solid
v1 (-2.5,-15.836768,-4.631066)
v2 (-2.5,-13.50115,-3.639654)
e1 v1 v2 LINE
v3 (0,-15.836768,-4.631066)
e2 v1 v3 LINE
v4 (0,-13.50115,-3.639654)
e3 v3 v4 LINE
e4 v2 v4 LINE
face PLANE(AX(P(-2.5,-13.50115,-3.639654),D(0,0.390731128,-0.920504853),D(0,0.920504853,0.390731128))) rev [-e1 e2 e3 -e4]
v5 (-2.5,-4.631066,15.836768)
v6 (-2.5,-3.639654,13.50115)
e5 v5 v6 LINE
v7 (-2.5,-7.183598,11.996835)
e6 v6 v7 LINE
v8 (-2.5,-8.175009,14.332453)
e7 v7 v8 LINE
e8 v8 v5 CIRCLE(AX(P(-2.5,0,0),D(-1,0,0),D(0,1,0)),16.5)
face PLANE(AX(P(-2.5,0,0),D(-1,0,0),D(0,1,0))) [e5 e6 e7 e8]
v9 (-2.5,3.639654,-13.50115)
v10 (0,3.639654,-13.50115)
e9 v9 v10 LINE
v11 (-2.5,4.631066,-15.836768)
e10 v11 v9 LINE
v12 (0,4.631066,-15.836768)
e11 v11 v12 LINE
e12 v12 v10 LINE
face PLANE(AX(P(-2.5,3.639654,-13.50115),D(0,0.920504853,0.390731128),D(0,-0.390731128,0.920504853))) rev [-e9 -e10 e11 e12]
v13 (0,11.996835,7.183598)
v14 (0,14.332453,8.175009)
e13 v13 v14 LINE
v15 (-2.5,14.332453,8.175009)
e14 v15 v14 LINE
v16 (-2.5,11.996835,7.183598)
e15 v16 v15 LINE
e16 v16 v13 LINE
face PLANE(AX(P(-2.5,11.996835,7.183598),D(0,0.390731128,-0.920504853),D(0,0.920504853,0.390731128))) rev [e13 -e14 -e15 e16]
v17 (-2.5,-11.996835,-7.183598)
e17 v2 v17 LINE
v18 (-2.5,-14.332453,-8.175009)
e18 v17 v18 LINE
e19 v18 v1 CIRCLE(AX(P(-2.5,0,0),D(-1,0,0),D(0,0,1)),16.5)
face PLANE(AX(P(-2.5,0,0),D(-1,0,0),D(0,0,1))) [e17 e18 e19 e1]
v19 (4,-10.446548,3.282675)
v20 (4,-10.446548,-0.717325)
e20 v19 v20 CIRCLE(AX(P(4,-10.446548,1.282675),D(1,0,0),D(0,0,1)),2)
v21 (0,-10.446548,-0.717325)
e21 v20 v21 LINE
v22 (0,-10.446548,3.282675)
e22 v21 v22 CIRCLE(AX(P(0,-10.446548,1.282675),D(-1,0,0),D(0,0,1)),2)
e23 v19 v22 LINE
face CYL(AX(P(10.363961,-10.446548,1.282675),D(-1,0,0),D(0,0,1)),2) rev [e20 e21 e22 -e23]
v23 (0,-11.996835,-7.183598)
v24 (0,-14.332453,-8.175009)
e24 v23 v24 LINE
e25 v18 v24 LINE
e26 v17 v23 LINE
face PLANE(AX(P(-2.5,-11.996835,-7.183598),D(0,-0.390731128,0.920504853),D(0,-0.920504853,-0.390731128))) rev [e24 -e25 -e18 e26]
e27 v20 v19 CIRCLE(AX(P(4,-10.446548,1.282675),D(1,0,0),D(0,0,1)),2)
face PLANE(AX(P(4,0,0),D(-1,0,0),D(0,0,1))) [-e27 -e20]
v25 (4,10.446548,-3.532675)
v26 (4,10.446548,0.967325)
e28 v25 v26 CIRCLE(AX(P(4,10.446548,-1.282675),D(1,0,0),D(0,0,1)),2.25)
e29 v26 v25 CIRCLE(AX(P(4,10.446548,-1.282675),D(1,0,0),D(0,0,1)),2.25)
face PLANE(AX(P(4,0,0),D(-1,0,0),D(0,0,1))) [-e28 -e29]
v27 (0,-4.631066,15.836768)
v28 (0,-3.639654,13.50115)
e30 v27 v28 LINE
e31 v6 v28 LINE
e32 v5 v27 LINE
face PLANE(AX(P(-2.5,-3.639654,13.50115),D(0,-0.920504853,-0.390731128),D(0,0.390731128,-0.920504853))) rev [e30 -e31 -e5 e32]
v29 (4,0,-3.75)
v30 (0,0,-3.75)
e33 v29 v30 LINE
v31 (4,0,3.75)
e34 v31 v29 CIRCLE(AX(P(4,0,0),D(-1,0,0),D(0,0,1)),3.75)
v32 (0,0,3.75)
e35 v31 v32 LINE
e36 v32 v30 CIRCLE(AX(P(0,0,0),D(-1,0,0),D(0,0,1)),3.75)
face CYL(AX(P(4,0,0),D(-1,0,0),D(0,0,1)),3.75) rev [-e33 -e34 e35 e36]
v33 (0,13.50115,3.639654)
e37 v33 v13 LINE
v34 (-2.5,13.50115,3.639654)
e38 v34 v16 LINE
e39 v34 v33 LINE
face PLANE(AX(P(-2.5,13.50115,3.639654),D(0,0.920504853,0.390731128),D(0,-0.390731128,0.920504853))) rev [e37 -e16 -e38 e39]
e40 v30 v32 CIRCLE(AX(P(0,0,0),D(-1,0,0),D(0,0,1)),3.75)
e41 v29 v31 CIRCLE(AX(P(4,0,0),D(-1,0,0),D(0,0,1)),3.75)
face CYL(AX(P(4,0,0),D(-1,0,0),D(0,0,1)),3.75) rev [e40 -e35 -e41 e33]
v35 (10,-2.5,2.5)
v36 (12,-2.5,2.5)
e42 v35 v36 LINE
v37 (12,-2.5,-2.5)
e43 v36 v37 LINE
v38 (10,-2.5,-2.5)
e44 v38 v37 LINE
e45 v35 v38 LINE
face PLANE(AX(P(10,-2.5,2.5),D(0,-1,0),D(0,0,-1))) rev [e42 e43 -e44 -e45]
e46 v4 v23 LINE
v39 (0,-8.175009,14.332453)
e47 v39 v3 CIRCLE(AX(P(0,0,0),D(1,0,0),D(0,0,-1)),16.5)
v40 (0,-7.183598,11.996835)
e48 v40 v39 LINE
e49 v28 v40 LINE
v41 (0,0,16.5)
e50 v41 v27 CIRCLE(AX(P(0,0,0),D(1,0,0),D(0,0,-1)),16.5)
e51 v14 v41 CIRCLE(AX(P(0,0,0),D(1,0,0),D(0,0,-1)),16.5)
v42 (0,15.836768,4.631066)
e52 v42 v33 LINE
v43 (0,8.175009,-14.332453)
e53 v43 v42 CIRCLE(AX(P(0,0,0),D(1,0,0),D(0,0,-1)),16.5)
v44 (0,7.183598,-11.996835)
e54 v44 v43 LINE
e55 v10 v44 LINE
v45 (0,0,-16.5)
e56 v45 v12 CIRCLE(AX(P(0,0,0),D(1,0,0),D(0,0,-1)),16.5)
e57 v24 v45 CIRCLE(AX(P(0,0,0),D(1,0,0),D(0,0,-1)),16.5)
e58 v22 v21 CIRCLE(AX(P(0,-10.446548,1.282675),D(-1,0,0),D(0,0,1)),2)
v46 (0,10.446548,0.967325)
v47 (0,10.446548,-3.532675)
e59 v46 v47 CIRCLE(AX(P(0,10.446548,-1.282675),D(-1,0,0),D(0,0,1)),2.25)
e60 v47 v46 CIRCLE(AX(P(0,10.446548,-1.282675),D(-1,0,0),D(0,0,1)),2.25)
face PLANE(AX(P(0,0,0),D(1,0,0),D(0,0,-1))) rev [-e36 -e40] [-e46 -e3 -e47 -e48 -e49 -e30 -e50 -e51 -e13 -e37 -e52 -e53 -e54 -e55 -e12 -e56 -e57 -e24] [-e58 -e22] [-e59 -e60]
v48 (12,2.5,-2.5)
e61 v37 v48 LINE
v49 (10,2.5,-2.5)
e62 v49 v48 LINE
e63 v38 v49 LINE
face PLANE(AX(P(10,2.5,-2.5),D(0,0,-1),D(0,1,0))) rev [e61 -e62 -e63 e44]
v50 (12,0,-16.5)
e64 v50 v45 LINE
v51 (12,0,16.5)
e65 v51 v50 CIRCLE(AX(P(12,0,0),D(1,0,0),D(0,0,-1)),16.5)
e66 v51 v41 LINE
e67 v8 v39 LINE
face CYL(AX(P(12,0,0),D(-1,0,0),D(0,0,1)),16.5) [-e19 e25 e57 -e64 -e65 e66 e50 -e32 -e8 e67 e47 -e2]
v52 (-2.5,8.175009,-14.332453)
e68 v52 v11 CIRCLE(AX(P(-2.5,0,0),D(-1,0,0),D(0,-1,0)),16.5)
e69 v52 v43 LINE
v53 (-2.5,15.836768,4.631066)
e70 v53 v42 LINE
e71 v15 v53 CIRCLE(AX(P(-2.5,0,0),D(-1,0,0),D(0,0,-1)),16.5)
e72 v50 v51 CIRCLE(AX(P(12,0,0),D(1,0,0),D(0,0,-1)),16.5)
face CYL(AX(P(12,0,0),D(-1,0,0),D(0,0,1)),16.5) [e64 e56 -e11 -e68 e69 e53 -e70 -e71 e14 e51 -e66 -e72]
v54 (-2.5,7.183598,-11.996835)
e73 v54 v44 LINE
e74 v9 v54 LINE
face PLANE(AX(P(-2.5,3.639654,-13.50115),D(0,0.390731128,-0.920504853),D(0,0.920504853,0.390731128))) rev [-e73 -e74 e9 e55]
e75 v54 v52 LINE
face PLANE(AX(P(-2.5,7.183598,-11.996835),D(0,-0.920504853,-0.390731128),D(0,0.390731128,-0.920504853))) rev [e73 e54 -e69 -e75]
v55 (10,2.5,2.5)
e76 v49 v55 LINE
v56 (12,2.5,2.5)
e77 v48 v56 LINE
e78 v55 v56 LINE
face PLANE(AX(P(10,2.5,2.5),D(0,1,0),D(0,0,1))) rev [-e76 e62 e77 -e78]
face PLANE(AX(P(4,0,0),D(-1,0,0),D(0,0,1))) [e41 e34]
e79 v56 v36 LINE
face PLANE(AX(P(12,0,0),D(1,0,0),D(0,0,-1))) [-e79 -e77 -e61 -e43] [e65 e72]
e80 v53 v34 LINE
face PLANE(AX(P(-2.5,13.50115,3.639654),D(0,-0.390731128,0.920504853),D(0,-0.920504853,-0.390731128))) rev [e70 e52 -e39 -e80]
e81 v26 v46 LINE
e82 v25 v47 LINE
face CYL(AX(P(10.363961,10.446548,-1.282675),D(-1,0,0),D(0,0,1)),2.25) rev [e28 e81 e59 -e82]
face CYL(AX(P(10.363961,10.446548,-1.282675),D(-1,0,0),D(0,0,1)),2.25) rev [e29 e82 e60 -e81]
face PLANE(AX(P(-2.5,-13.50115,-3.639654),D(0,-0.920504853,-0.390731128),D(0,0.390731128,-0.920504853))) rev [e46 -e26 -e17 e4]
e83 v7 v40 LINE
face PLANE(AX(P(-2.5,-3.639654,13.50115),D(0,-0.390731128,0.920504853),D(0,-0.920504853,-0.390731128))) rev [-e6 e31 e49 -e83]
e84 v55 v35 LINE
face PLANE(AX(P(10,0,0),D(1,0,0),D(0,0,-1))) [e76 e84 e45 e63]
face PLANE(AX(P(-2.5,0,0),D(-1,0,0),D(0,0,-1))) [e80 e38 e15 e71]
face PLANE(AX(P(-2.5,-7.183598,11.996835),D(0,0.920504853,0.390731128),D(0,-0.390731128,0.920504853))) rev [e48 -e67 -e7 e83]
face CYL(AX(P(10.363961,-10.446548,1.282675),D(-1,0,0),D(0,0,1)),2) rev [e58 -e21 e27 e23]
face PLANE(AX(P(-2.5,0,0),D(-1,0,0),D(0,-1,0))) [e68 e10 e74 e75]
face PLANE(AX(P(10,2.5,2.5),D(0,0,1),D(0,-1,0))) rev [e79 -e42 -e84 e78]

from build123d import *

# Parameters (mm, degrees)
SKETCH_1_R               = 16.5
EXTRUDE_1_DEPTH          = 12
SKETCH_2_R               = 3.75
CUT_EXTRUDE_1_DEPTH      = 4
EXTRUDE_START            = 2.5
EXTRUDE_2_DEPTH          = 2.5
PATTERN_CIRCULAR_1_COUNT = 4
SKETCH_4_R               = 2.25
SKETCH_4_R_2             = 2
CUT_EXTRUDE_2_DEPTH      = 4
SKETCH_5_W               = 5
SKETCH_5_H               = 5
CUT_EXTRUDE_3_DEPTH      = 2


with BuildPart() as part:
    # 草图1 → 凸台-拉伸1 (new body)
    with BuildSketch(Plane(origin=(0, 0, 0), x_dir=(0, 0, -1), z_dir=(1, 0, 0))):
        Circle(SKETCH_1_R)
    extrude(amount=EXTRUDE_1_DEPTH)

    # 草图2 → 切除-拉伸1 (cut)
    with BuildSketch(Plane.ZY):
        Circle(SKETCH_2_R)
    extrude(amount=-CUT_EXTRUDE_1_DEPTH, mode=Mode.SUBTRACT)

    # 草图3 → 凸台-拉伸2 (add)
    with BuildSketch(Plane.ZY.offset(EXTRUDE_START)):
        with BuildLine():
            Line((-3.639654287, -13.501149643), (-4.631065603, -15.836768338))
            ThreePointArc((-4.631065603, -15.836768338), (-6.44706362, -15.188330082), (-8.175009289, -14.332453493))
            Line((-8.175009289, -14.332453493), (-7.183597972, -11.996834798))
            Line((-7.183597972, -11.996834798), (-3.639654287, -13.501149643))
        make_face()
    extrude_2 = extrude(amount=-EXTRUDE_2_DEPTH)

    # 阵列(圆周)1: 凸台-拉伸2 ×4 about axis
    pattern_circular_1_axis = Axis((0, 0, 0), (1, 0, 0))
    for i in range(1, PATTERN_CIRCULAR_1_COUNT):
        add(extrude_2.rotate(pattern_circular_1_axis, i * 360 / PATTERN_CIRCULAR_1_COUNT))

    # 草图4 → 切除-拉伸2 (cut)
    with BuildSketch(Plane.ZY):
        with Locations((-1.282674839, 10.446548246)):
            Circle(SKETCH_4_R)
        with Locations((1.282674839, -10.446548246)):
            Circle(SKETCH_4_R_2)
    extrude(amount=-CUT_EXTRUDE_2_DEPTH, mode=Mode.SUBTRACT)

    # 草图5 → 切除-拉伸3 (cut)
    with BuildSketch(Plane(origin=(12, 0, 0), x_dir=(0, 0, -1), z_dir=(1, 0, 0))):
        Rectangle(SKETCH_5_W, SKETCH_5_H)
    extrude(amount=-CUT_EXTRUDE_3_DEPTH, mode=Mode.SUBTRACT)


solid = part.part
